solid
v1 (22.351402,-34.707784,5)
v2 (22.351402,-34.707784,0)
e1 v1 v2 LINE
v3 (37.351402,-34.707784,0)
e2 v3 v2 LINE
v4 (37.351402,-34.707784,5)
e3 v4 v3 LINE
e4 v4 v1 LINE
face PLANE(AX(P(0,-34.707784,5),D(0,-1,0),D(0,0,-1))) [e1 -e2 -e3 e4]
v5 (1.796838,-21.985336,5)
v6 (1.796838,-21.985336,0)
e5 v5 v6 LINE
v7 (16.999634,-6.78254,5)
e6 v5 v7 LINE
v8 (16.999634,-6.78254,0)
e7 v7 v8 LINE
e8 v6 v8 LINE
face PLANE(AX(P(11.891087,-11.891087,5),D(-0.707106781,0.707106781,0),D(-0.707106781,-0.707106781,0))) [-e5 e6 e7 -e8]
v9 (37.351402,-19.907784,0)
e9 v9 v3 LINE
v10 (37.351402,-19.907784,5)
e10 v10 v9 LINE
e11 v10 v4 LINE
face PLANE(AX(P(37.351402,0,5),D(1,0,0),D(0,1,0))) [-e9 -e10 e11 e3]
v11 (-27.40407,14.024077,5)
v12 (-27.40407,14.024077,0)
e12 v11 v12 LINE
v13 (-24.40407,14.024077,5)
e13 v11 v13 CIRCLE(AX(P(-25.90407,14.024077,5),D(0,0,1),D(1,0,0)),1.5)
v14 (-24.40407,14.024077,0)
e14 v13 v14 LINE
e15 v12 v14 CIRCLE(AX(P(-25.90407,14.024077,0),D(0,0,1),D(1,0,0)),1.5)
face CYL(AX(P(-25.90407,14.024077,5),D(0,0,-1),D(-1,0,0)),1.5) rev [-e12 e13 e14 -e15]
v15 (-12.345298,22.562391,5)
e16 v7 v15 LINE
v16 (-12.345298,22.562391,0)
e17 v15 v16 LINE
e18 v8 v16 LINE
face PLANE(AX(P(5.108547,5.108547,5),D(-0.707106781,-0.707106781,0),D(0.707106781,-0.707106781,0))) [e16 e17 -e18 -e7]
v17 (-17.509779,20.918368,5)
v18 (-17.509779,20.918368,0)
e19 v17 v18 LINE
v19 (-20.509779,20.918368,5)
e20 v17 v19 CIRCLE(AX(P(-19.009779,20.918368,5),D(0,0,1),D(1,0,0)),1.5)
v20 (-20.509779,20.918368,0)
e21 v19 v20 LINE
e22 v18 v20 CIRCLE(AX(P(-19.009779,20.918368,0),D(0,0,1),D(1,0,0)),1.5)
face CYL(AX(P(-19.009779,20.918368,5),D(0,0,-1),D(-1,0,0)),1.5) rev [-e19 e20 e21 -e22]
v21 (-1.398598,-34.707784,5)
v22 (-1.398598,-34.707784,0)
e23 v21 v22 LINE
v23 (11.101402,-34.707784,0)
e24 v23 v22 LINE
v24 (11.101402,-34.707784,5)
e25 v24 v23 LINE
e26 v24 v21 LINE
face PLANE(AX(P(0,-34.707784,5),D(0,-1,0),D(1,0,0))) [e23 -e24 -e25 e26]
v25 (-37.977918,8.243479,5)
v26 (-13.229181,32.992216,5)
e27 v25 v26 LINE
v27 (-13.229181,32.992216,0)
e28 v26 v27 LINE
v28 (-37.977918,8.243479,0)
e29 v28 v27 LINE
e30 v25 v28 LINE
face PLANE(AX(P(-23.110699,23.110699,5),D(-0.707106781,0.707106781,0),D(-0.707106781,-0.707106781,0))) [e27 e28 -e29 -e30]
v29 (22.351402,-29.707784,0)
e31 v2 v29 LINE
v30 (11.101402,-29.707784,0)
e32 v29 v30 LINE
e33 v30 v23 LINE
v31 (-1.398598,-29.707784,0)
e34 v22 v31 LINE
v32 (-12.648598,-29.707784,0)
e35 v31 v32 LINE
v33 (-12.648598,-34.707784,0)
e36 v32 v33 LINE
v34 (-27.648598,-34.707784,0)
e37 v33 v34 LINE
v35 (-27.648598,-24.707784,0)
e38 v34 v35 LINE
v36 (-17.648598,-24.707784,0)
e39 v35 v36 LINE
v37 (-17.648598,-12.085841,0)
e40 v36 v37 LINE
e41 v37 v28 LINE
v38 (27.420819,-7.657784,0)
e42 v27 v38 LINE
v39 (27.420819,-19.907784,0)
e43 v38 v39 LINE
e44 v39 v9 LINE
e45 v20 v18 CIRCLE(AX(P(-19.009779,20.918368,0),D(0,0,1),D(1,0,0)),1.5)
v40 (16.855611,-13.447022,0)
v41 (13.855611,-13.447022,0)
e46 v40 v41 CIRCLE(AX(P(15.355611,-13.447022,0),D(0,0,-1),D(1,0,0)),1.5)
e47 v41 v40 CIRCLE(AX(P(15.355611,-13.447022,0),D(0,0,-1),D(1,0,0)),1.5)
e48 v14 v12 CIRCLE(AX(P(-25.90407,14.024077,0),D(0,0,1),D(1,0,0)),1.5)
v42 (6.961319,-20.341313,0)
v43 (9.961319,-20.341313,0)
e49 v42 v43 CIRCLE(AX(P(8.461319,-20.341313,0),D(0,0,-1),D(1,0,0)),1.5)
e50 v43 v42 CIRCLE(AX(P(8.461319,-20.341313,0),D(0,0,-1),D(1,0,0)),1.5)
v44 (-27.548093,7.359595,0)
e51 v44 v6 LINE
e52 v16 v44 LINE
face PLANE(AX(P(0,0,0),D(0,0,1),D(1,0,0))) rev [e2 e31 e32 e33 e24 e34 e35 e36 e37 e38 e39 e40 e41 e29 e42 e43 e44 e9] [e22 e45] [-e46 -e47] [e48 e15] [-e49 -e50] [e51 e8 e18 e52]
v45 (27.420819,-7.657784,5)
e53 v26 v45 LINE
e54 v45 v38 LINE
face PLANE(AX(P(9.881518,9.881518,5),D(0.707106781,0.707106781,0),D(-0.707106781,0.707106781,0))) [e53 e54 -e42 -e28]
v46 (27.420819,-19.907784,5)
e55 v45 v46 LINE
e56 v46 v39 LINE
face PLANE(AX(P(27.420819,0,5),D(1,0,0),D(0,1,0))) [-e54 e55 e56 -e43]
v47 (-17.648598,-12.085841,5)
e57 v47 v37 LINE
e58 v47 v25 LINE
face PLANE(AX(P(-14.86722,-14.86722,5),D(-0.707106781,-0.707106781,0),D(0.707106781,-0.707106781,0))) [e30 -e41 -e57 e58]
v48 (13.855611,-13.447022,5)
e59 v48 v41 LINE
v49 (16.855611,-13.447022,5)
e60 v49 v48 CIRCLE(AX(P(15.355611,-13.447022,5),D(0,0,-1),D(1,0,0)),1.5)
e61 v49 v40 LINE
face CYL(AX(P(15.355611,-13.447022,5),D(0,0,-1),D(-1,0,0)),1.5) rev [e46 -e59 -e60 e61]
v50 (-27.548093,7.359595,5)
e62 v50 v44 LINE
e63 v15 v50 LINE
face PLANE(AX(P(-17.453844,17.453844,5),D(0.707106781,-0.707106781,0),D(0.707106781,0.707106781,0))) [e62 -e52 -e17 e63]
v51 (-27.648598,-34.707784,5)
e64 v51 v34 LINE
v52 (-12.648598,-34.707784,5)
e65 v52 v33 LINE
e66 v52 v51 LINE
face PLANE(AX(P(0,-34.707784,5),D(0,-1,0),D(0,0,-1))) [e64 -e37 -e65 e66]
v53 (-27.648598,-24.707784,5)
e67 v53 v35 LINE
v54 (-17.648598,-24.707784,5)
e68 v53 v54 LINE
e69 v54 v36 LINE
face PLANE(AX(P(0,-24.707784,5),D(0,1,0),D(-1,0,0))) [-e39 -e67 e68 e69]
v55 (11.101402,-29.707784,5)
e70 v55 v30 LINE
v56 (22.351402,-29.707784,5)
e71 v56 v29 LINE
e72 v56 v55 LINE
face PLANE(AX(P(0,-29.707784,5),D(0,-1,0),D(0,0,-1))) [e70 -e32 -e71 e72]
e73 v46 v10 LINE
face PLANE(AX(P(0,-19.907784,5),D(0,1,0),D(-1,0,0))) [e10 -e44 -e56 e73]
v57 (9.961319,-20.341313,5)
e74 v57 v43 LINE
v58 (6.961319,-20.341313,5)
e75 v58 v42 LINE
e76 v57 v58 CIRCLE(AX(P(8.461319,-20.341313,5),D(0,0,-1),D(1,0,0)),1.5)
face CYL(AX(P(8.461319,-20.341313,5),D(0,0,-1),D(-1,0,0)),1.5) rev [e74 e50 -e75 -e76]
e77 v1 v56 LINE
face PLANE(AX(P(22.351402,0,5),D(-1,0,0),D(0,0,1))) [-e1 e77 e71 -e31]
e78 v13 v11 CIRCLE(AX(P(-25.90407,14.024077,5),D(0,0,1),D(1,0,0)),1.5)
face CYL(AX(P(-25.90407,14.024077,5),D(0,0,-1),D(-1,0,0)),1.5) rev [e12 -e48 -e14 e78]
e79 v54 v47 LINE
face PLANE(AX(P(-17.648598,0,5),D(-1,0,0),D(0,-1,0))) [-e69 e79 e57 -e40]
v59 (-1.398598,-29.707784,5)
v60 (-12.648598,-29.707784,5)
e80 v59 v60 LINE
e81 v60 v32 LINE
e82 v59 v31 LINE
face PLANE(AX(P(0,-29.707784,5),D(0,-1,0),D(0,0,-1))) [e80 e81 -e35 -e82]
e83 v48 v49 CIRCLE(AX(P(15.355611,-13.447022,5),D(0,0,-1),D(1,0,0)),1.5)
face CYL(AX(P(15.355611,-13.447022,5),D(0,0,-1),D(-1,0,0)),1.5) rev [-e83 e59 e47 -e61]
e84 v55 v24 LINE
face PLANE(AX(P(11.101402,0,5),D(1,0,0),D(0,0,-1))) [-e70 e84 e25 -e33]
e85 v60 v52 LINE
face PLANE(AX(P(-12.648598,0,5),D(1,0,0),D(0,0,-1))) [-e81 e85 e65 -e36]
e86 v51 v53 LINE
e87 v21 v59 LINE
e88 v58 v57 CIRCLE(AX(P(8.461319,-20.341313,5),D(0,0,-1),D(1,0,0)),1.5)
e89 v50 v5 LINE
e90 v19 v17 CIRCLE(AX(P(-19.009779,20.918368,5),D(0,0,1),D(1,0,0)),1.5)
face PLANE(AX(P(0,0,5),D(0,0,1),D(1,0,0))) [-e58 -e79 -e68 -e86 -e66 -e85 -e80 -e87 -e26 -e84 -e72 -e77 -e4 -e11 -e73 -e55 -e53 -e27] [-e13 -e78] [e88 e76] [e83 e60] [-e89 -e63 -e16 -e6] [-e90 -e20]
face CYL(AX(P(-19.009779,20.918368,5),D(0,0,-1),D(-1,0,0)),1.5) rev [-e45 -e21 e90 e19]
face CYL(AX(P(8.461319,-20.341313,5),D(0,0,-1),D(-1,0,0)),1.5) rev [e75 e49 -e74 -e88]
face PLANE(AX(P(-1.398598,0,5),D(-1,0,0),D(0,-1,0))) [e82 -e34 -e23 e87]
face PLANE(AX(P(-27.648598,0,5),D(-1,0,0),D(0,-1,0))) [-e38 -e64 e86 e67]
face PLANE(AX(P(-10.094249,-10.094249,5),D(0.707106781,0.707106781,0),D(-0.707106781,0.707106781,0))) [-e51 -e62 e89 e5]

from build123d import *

# Parameters (mm, degrees)
SKETCH_1_R      = 1.5
EXTRUDE_1_DEPTH = 5


with BuildPart() as part:
    # 草图1 → 凸台-拉伸1 (new body)
    with BuildSketch(Plane.XY):
        Polygon((-12.648598414, -34.707783696), (-27.648598414, -34.707783696), (-27.648598414, -24.707783696), (-17.648598414, -24.707783696), (-17.648598414, -12.085840997), (-37.977918373, 8.243478962), (-13.229181032, 32.992216304), (27.420818968, -7.657783696), (27.420818968, -19.907783696), (37.351401586, -19.907783696), (37.351401586, -34.707783696), (22.351401586, -34.707783696), (22.351401586, -29.707783696), (11.101401586, -29.707783696), (11.101401586, -34.707783696), (-1.398598414, -34.707783696), (-1.398598414, -29.707783696), (-12.648598414, -29.707783696), align=None)
        with Locations((-19.009778968, 20.918368015)):
            Circle(SKETCH_1_R, mode=Mode.SUBTRACT)
        with Locations((-25.904070084, 14.024076898)):
            Circle(SKETCH_1_R, mode=Mode.SUBTRACT)
        with Locations((15.355610598, -13.447021551)):
            Circle(SKETCH_1_R, mode=Mode.SUBTRACT)
        with Locations((8.461319481, -20.341312667)):
            Circle(SKETCH_1_R, mode=Mode.SUBTRACT)
        Polygon((-27.548093351, 7.359595486), (1.796838069, -21.985335933), (16.999633864, -6.782540138), (-12.345297555, 22.562391281), align=None, mode=Mode.SUBTRACT)
    extrude(amount=EXTRUDE_1_DEPTH)


solid = part.part
